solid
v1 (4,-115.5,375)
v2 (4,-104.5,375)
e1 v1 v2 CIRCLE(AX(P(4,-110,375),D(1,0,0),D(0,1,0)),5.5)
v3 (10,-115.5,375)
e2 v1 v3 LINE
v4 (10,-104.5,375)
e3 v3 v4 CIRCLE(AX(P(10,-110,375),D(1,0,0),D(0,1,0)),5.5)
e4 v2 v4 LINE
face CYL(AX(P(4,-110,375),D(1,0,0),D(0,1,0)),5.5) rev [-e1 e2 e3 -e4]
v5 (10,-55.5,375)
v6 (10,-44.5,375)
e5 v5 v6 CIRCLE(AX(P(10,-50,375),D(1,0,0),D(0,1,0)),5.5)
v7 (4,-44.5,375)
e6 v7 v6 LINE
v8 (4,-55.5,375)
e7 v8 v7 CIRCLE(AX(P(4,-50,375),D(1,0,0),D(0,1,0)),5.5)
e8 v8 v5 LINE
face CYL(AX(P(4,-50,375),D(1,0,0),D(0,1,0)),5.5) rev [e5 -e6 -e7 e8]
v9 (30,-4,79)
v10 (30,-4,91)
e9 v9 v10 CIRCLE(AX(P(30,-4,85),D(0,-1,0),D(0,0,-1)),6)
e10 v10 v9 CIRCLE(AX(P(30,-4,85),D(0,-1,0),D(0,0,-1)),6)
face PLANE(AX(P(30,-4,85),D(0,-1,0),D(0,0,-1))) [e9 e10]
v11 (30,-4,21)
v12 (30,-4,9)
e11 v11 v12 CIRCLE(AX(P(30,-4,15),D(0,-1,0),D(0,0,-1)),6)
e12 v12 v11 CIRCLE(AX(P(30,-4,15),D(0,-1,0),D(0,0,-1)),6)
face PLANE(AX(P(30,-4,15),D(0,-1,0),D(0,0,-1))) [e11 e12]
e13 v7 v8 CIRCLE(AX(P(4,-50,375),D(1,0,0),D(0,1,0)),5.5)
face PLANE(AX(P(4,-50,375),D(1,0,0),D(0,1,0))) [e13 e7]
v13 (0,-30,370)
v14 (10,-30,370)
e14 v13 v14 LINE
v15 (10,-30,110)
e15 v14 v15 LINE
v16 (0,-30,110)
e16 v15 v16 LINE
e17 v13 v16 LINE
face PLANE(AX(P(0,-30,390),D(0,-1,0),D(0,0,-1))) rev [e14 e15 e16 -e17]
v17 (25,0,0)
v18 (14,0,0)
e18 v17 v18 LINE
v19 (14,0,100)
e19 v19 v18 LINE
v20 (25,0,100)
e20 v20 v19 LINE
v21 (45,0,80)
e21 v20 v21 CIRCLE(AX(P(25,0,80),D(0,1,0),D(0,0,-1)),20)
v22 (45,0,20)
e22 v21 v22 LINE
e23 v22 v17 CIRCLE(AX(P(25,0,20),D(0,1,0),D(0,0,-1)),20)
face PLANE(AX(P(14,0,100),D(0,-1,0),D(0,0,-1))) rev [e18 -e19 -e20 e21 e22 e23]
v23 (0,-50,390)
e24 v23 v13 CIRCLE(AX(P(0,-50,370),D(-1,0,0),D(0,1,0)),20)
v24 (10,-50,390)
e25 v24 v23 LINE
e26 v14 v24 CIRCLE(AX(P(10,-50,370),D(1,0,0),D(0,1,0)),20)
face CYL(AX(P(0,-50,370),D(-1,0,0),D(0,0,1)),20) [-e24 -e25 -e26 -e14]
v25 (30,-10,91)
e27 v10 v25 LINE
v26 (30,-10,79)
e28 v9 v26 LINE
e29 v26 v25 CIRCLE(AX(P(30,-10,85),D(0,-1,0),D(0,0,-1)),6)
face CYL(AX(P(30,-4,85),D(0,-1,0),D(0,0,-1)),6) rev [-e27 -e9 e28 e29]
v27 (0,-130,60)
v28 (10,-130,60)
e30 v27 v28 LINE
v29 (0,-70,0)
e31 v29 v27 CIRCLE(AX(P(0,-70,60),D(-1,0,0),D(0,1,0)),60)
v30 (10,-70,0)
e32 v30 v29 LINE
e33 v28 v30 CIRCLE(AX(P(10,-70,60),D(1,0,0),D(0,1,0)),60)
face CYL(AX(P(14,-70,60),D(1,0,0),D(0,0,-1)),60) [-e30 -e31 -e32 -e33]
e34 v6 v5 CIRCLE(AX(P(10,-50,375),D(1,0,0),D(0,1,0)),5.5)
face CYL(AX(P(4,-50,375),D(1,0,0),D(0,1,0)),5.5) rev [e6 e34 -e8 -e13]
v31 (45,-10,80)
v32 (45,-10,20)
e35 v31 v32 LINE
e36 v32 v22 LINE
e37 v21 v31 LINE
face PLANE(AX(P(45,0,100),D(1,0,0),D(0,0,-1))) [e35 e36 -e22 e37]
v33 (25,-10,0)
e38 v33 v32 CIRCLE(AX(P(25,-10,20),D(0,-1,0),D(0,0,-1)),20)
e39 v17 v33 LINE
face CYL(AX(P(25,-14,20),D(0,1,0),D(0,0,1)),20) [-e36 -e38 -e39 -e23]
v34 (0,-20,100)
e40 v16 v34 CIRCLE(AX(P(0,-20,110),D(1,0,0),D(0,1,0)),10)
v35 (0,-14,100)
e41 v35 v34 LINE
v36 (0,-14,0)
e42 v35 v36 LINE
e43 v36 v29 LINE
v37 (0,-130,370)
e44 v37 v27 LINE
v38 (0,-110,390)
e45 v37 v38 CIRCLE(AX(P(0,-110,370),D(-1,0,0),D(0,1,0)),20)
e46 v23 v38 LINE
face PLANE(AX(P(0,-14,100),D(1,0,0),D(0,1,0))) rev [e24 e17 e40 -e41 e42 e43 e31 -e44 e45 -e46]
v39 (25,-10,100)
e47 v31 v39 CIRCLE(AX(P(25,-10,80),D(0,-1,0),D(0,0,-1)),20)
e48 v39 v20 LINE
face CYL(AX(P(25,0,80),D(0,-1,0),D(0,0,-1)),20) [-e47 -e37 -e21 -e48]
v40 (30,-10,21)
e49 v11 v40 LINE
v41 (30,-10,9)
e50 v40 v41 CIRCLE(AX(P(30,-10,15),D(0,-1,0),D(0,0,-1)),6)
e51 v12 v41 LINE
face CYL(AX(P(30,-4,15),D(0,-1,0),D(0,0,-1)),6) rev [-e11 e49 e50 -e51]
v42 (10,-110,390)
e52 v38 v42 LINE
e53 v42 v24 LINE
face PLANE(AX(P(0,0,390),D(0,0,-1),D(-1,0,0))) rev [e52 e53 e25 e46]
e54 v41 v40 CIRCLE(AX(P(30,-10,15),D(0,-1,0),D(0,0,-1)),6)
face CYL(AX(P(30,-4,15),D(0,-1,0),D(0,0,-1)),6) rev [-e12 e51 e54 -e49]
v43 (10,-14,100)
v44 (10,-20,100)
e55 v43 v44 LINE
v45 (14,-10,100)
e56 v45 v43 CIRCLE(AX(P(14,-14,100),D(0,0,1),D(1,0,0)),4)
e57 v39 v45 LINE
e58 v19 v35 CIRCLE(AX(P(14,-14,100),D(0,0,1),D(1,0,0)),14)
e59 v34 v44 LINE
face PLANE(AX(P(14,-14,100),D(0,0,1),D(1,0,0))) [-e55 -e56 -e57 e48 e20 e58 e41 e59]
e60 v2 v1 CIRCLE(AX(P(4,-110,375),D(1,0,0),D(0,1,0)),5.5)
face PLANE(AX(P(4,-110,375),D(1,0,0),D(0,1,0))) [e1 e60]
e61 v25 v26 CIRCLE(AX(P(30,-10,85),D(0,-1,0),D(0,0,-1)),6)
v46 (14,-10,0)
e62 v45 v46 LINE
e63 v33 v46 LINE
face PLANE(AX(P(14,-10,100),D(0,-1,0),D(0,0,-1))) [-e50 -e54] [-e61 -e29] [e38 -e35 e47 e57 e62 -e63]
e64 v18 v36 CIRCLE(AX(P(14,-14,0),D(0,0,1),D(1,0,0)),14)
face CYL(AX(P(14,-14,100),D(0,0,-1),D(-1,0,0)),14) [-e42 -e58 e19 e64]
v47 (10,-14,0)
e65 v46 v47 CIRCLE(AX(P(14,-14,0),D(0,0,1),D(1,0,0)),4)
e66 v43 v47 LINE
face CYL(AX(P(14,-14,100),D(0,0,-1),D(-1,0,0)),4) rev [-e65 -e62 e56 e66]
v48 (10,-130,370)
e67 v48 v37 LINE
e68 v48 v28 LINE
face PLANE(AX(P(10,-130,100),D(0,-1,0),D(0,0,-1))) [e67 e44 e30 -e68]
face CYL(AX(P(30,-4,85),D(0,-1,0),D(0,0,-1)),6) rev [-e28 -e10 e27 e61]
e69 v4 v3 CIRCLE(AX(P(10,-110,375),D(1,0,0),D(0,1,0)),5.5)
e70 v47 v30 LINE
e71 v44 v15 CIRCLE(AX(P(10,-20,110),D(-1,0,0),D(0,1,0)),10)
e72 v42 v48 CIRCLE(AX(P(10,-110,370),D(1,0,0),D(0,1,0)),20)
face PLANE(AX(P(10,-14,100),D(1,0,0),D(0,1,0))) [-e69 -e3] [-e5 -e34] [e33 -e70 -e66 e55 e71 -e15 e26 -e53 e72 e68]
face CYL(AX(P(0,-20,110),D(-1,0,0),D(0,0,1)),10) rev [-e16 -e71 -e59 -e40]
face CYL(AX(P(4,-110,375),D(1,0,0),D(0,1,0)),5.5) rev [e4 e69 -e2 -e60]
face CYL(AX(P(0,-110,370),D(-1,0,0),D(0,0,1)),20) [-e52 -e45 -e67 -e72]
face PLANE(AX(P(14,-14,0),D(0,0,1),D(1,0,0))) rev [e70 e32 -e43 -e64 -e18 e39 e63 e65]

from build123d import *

# Parameters (mm, degrees)
EXTRUDE_THIN1_DEPTH = 100
SKETCH2_W           = 10
SKETCH2_H           = 100
BOSS_EXTRUDE1_DEPTH = 290
FILLET1_R           = 10
FILLET3_R           = 20
FILLET4_R           = 60
SKETCH3_R           = 6
CUT_EXTRUDE1_DEPTH  = 6
LPATTERN1_COUNT     = 2
LPATTERN1_PITCH     = 70
SKETCH4_R           = 5.5
CUT_EXTRUDE2_DEPTH  = 6
LPATTERN2_COUNT     = 2
LPATTERN2_PITCH     = 60


with BuildPart() as part:
    # Sketch1 → Extrude-Thin1 (new body)
    with BuildSketch(Plane.XY):
        with BuildLine():
            Line((0, -130), (0, -14))
            ThreePointArc((0, -14), (4.100505063, -4.100505063), (14, 0))
            Line((14, 0), (45, 0))
            Line((45, 0), (45, -10))
            Line((45, -10), (14, -10))
            ThreePointArc((14, -10), (11.171572875, -11.171572875), (10, -14))
            Line((10, -14), (10, -130))
            Line((10, -130), (0, -130))
        make_face()
    extrude(amount=EXTRUDE_THIN1_DEPTH)

    # Sketch2 → Boss-Extrude1 (add)
    with BuildSketch(Plane.XY.offset(100)):
        with Locations((5, -80)):
            Rectangle(SKETCH2_W, SKETCH2_H)
    extrude(amount=BOSS_EXTRUDE1_DEPTH)

    # Fillet1
    fillet1_edges = [part.edges().sort_by_distance(p)[0] for p in [
        (5, -30, 100),
    ]]
    fillet(fillet1_edges, radius=FILLET1_R)

    # Fillet3
    fillet3_edges = [part.edges().sort_by_distance(p)[0] for p in [
        (5, -30, 390),
        (5, -130, 390),
        (45, -5, 0),
        (45, -5, 100),
    ]]
    fillet(fillet3_edges, radius=FILLET3_R)

    # Fillet4
    fillet4_edges = [part.edges().sort_by_distance(p)[0] for p in [
        (5, -130, 0),
    ]]
    fillet(fillet4_edges, radius=FILLET4_R)

    # Sketch3 → Cut-Extrude1 (cut)
    with BuildSketch(Plane.XZ.offset(10)):
        with Locations(Location((30, 15, 0), (0, 0, 270))):
            Circle(SKETCH3_R)
    cut_extrude1 = extrude(amount=-CUT_EXTRUDE1_DEPTH, mode=Mode.SUBTRACT)

    # LPattern1: Cut-Extrude1 ×2
    with Locations(*[(0, 0, i * LPATTERN1_PITCH) for i in range(1, LPATTERN1_COUNT)]):
        add(cut_extrude1, mode=Mode.SUBTRACT)

    # Sketch4 → Cut-Extrude2 (cut)
    with BuildSketch(Plane(origin=(10, 0, 0), x_dir=(0, 0, -1), z_dir=(1, 0, 0))):
        with Locations(Location((-375, -50, 0), (0, 0, 90))):
            Circle(SKETCH4_R)
    cut_extrude2 = extrude(amount=-CUT_EXTRUDE2_DEPTH, mode=Mode.SUBTRACT)

    # LPattern2: Cut-Extrude2 ×2
    with Locations(*[(0, -i * LPATTERN2_PITCH, 0) for i in range(1, LPATTERN2_COUNT)]):
        add(cut_extrude2, mode=Mode.SUBTRACT)


solid = part.part
